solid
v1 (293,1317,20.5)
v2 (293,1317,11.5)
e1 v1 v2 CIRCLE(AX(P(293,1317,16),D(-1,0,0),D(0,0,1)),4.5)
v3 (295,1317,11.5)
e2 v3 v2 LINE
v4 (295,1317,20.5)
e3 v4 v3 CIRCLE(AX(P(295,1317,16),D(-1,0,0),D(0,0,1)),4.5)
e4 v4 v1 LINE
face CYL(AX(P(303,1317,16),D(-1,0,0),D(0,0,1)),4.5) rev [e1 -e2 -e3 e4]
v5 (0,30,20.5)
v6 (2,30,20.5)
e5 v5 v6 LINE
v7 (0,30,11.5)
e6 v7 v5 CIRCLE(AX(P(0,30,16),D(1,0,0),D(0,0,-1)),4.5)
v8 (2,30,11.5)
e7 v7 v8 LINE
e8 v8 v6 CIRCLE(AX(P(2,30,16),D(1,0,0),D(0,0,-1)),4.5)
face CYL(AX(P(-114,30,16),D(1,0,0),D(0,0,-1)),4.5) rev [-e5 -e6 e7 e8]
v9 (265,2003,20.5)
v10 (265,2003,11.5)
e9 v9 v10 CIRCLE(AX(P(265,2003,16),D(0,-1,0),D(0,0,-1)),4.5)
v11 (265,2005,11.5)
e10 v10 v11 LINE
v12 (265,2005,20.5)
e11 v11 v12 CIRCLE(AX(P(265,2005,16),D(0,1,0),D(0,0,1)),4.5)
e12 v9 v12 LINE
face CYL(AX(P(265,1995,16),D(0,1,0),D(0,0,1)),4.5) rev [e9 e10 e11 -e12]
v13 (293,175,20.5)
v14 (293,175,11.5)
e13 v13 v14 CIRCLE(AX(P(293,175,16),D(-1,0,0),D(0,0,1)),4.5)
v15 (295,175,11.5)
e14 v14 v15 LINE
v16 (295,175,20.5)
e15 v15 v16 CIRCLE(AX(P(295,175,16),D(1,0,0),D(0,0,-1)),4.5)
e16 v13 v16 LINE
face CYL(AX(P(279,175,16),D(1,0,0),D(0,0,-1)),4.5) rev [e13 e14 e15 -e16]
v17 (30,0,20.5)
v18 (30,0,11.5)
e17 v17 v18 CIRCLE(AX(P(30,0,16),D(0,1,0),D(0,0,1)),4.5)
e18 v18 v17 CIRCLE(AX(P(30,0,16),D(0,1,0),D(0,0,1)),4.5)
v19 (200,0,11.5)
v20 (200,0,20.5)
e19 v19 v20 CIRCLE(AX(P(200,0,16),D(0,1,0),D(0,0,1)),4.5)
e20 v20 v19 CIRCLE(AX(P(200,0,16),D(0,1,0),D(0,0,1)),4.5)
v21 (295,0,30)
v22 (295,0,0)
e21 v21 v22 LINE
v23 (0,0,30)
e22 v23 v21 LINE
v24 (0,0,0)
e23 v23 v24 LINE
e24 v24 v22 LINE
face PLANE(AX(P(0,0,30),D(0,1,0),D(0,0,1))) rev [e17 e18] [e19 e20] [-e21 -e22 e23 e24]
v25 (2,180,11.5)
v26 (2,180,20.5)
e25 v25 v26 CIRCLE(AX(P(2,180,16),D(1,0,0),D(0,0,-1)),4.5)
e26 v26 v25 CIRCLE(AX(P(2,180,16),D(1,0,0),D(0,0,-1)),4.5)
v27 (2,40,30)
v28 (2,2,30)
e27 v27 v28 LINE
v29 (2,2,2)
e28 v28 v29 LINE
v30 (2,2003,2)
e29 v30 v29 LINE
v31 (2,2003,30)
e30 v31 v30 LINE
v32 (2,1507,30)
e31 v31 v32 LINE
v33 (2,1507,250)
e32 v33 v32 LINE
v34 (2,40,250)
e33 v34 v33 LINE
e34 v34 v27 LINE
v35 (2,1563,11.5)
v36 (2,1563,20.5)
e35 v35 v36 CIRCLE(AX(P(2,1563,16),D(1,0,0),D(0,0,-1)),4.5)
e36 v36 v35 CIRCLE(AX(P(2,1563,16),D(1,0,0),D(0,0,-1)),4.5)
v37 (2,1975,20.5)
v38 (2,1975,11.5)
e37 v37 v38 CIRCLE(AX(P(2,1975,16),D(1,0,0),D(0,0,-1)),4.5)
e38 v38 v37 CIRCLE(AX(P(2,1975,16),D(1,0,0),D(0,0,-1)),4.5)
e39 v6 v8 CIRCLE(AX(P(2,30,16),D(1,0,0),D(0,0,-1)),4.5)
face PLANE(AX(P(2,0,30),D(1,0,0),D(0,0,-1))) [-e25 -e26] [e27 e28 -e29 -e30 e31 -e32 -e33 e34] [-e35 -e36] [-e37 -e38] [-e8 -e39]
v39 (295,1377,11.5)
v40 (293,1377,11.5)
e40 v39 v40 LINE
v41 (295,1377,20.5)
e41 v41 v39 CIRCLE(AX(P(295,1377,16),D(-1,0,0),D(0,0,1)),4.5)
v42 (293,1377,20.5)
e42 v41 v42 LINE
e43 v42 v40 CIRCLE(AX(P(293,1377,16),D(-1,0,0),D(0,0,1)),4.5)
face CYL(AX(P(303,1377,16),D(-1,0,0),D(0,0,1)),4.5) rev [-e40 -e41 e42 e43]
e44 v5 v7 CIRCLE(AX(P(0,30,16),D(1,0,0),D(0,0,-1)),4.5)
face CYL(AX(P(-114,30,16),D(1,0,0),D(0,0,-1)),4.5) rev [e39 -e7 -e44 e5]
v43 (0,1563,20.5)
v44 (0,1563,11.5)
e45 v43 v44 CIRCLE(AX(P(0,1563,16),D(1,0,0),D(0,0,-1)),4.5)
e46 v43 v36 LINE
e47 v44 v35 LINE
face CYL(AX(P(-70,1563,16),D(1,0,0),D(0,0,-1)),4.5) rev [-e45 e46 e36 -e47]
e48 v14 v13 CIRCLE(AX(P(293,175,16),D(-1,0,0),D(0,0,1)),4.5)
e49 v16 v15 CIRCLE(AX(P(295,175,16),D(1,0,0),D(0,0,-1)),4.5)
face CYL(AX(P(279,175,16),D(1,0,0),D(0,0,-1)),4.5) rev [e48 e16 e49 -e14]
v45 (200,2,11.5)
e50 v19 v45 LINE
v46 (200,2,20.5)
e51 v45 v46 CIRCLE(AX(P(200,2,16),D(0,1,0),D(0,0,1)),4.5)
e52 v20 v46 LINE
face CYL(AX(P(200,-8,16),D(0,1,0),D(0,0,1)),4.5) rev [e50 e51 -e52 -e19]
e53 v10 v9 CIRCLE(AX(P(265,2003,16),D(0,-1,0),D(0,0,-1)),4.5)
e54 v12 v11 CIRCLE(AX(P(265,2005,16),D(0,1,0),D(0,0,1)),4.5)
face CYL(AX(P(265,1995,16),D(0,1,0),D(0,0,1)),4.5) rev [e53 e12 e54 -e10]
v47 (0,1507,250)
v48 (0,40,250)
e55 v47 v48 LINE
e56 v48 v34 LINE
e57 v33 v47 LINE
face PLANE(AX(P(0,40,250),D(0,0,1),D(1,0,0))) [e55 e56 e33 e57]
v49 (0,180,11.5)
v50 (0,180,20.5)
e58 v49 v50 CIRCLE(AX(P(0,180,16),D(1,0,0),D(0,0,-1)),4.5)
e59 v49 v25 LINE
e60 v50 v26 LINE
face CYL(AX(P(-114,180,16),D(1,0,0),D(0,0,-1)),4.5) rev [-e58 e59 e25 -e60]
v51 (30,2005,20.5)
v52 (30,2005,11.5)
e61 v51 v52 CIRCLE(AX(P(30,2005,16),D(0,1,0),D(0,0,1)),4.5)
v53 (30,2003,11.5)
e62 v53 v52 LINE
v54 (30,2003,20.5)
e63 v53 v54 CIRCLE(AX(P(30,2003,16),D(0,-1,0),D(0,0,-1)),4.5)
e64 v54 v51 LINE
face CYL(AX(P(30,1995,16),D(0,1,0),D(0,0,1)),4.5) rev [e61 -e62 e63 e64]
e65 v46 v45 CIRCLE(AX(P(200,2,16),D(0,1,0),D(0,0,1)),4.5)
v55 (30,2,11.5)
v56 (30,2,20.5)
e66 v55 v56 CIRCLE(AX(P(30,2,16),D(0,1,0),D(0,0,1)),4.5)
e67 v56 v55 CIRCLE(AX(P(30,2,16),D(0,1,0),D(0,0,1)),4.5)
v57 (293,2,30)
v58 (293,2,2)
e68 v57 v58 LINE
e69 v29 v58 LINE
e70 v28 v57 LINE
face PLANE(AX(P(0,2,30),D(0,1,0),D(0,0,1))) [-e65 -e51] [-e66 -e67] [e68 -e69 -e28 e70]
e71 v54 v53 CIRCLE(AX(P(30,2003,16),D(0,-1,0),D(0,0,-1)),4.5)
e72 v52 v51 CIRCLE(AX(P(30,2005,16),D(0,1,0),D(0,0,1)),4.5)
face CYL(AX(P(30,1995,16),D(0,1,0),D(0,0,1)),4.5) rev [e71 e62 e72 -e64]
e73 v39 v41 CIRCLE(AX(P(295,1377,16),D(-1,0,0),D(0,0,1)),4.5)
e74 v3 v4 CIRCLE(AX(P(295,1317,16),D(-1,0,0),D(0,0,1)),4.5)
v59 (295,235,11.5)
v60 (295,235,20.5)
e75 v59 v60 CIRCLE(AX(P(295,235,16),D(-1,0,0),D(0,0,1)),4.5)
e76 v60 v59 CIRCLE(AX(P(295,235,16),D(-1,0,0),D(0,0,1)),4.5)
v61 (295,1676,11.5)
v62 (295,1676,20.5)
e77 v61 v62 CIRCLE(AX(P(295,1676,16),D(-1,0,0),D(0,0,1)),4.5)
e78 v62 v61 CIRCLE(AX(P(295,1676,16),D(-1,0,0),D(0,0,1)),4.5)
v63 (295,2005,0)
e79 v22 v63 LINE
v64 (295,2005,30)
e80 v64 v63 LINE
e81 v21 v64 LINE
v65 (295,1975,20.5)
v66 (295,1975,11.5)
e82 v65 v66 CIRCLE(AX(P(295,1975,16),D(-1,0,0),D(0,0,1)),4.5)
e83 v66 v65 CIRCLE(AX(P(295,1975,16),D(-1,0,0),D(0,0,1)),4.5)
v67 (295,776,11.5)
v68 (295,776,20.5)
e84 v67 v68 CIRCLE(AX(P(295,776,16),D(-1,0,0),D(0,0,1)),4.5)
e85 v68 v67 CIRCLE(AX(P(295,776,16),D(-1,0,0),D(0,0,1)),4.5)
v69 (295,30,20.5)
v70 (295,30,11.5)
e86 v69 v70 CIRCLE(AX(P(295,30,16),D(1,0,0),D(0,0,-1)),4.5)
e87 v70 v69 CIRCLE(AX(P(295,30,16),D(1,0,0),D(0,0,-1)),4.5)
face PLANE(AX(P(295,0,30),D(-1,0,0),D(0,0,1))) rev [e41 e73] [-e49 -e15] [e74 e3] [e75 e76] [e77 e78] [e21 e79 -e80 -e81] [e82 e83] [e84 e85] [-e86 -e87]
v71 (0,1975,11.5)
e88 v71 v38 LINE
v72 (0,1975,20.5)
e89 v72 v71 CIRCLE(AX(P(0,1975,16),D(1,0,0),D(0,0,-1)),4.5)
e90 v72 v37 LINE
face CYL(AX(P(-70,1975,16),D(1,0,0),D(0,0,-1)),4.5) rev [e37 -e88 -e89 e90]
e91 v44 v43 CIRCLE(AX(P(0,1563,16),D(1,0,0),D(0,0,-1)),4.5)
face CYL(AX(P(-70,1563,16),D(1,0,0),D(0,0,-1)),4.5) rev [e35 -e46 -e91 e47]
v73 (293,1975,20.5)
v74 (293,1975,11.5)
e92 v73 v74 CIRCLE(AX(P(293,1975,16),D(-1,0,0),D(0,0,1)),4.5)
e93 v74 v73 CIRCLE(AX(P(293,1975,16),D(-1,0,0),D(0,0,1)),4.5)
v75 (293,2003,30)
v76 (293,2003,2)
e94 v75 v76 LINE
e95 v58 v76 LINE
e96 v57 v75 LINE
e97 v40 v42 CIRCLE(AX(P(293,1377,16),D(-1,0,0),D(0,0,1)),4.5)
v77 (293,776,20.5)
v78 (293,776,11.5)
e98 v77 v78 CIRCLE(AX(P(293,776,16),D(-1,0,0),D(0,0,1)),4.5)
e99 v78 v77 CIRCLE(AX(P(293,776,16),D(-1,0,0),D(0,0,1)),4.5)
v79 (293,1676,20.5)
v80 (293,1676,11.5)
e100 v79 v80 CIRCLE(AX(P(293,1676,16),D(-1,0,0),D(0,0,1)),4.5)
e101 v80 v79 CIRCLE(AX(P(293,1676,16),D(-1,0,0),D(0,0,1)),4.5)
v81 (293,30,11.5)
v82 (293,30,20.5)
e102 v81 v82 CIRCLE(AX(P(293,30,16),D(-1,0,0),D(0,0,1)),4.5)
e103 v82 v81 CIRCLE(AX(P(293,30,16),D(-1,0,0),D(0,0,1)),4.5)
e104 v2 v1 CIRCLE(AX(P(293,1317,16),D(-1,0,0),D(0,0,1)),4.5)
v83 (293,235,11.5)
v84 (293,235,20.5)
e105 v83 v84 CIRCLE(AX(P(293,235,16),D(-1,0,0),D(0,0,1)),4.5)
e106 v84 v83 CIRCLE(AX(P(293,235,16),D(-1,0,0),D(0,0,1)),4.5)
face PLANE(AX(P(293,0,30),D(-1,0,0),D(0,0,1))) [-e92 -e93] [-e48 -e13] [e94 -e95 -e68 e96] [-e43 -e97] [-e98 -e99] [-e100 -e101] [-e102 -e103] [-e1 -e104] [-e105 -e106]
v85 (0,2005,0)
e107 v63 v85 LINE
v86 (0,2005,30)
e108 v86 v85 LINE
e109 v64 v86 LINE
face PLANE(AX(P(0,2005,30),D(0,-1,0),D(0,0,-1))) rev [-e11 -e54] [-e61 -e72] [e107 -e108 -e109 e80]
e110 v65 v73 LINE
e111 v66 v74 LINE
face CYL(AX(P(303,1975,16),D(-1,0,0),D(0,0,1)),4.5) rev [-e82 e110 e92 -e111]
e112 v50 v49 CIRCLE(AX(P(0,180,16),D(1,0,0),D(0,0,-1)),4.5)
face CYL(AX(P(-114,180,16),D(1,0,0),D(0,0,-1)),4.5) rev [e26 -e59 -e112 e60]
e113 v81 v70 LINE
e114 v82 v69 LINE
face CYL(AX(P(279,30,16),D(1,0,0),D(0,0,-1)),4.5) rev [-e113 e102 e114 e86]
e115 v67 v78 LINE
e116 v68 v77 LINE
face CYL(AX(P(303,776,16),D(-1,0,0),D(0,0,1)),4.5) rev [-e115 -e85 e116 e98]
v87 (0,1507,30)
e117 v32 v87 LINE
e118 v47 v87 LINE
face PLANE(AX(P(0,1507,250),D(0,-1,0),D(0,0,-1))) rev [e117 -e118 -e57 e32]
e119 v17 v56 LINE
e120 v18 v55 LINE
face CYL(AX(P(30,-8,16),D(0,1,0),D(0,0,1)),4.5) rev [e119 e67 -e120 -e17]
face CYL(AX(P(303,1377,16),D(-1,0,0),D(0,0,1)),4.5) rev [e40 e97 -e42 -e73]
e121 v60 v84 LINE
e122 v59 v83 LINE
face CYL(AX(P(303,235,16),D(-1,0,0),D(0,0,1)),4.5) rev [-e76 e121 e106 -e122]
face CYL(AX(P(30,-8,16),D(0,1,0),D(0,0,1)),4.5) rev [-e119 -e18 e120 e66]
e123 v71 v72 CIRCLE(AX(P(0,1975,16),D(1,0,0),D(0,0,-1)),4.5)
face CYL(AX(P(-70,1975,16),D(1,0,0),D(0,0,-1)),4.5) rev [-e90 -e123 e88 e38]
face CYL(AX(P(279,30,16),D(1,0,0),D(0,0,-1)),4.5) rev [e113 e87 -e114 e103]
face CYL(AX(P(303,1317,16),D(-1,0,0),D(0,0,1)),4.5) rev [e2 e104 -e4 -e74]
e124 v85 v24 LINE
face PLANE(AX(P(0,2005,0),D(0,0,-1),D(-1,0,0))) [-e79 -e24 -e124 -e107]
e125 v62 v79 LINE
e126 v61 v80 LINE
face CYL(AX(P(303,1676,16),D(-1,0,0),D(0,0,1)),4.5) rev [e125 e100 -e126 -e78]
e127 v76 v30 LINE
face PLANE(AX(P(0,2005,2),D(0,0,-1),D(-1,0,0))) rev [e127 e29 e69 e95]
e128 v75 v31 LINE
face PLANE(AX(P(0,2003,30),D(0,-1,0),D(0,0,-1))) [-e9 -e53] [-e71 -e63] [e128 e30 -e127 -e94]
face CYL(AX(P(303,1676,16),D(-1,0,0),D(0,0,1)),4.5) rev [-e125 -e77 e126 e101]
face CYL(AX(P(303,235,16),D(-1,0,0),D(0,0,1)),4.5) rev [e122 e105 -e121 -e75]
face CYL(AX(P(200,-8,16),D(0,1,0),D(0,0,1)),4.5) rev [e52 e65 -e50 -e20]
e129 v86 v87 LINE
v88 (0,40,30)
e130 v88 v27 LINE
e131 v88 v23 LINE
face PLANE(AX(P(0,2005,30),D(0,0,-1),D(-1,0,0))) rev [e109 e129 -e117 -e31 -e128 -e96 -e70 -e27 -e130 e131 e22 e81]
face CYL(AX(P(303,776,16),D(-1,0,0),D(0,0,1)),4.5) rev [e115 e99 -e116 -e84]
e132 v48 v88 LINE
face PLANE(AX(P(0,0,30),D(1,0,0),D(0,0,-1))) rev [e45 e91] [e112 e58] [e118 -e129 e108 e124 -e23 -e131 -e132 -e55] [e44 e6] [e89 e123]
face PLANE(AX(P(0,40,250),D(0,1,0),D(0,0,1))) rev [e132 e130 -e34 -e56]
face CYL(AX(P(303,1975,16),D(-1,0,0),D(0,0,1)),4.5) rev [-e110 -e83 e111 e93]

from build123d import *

# Parameters (mm, degrees)
SKETCH_1_W          = 295
SKETCH_1_H          = 2005
EXTRUDE_1_DEPTH     = 30
SHELL_1_T           = -2
SKETCH_2_W          = 2
SKETCH_2_H          = 1467
EXTRUDE_2_DEPTH     = 220
SKETCH_3_R          = 4.5
CUT_EXTRUDE_1_DEPTH = 10
SKETCH_4_R          = 4.5
CUT_EXTRUDE_2_DEPTH = 116
SKETCH_5_R          = 4.5
CUT_EXTRUDE_3_DEPTH = 72
SKETCH_6_R          = 4.5
CUT_EXTRUDE_4_DEPTH = 10
CUT_EXTRUDE_START   = -10
SKETCH_7_R          = 4.5
CUT_EXTRUDE_5_DEPTH = 10
SKETCH_8_R          = 4.5
CUT_EXTRUDE_6_DEPTH = 16


with BuildPart() as part:
    # 草图1 → 凸台-拉伸1 (new body)
    with BuildSketch(Plane.XY):
        with Locations((147.5, 1002.5)):
            Rectangle(SKETCH_1_W, SKETCH_1_H)
    extrude(amount=EXTRUDE_1_DEPTH)

    # 抽壳1
    shell_1_openings = [part.faces().sort_by_distance(p)[0] for p in [
        (147.5, 1002.5, 30),
    ]]
    offset(amount=SHELL_1_T, openings=shell_1_openings, kind=Kind.INTERSECTION)

    # 草图2 → 凸台-拉伸2 (add)
    with BuildSketch(Plane.XY.offset(30)):
        with Locations((1, 773.5)):
            Rectangle(SKETCH_2_W, SKETCH_2_H)
    extrude(amount=EXTRUDE_2_DEPTH)

    # 草图3 → 切除-拉伸1 (cut)
    with BuildSketch(Plane(origin=(0, 2, 0), x_dir=(1, 0, 0), z_dir=(0, 1, 0))):
        with Locations(Location((30, -16, 0), (0, 0, 270))):
            Circle(SKETCH_3_R)
        with Locations(Location((200, -16, 0), (0, 0, 270))):
            Circle(SKETCH_3_R)
    extrude(amount=-CUT_EXTRUDE_1_DEPTH, mode=Mode.SUBTRACT)

    # 草图4 → 切除-拉伸2 (cut)
    with BuildSketch(Plane(origin=(2, 0, 0), x_dir=(0, 0, -1), z_dir=(1, 0, 0))):
        with Locations((-16, 30)):
            Circle(SKETCH_4_R)
        with Locations((-16, 180)):
            Circle(SKETCH_4_R)
    extrude(amount=-CUT_EXTRUDE_2_DEPTH, mode=Mode.SUBTRACT)

    # 草图5 → 切除-拉伸3 (cut)
    with BuildSketch(Plane(origin=(2, 0, 0), x_dir=(0, 0, -1), z_dir=(1, 0, 0))):
        with Locations((-16, 1975)):
            Circle(SKETCH_5_R)
        with Locations((-16, 1563)):
            Circle(SKETCH_5_R)
    extrude(amount=-CUT_EXTRUDE_3_DEPTH, mode=Mode.SUBTRACT)

    # 草图6 → 切除-拉伸4 (cut)
    with BuildSketch(Plane(origin=(0, 2005, 0), x_dir=(1, 0, 0), z_dir=(0, 1, 0))):
        with Locations(Location((30, -16, 0), (0, 0, 270))):
            Circle(SKETCH_6_R)
        with Locations(Location((265, -16, 0), (0, 0, 270))):
            Circle(SKETCH_6_R)
    extrude(amount=-CUT_EXTRUDE_4_DEPTH, mode=Mode.SUBTRACT)

    # 草图7 → 切除-拉伸5 (cut)
    with BuildSketch(Plane.ZY.offset(-293).offset(CUT_EXTRUDE_START)):
        with Locations(Location((16, 1975, 0), (0, 0, 180))):
            Circle(SKETCH_7_R)
        with Locations((16, 1676)):
            Circle(SKETCH_7_R)
        with Locations((16, 1377)):
            Circle(SKETCH_7_R)
        with Locations((16, 1317)):
            Circle(SKETCH_7_R)
        with Locations((16, 776)):
            Circle(SKETCH_7_R)
        with Locations((16, 235)):
            Circle(SKETCH_7_R)
    extrude(amount=CUT_EXTRUDE_5_DEPTH, mode=Mode.SUBTRACT)

    # 草图8 → 切除-拉伸6 (cut)
    with BuildSketch(Plane(origin=(295, 0, 0), x_dir=(0, 0, -1), z_dir=(1, 0, 0))):
        with Locations((-16, 30)):
            Circle(SKETCH_8_R)
        with Locations((-16, 175)):
            Circle(SKETCH_8_R)
    extrude(amount=-CUT_EXTRUDE_6_DEPTH, mode=Mode.SUBTRACT)


solid = part.part
